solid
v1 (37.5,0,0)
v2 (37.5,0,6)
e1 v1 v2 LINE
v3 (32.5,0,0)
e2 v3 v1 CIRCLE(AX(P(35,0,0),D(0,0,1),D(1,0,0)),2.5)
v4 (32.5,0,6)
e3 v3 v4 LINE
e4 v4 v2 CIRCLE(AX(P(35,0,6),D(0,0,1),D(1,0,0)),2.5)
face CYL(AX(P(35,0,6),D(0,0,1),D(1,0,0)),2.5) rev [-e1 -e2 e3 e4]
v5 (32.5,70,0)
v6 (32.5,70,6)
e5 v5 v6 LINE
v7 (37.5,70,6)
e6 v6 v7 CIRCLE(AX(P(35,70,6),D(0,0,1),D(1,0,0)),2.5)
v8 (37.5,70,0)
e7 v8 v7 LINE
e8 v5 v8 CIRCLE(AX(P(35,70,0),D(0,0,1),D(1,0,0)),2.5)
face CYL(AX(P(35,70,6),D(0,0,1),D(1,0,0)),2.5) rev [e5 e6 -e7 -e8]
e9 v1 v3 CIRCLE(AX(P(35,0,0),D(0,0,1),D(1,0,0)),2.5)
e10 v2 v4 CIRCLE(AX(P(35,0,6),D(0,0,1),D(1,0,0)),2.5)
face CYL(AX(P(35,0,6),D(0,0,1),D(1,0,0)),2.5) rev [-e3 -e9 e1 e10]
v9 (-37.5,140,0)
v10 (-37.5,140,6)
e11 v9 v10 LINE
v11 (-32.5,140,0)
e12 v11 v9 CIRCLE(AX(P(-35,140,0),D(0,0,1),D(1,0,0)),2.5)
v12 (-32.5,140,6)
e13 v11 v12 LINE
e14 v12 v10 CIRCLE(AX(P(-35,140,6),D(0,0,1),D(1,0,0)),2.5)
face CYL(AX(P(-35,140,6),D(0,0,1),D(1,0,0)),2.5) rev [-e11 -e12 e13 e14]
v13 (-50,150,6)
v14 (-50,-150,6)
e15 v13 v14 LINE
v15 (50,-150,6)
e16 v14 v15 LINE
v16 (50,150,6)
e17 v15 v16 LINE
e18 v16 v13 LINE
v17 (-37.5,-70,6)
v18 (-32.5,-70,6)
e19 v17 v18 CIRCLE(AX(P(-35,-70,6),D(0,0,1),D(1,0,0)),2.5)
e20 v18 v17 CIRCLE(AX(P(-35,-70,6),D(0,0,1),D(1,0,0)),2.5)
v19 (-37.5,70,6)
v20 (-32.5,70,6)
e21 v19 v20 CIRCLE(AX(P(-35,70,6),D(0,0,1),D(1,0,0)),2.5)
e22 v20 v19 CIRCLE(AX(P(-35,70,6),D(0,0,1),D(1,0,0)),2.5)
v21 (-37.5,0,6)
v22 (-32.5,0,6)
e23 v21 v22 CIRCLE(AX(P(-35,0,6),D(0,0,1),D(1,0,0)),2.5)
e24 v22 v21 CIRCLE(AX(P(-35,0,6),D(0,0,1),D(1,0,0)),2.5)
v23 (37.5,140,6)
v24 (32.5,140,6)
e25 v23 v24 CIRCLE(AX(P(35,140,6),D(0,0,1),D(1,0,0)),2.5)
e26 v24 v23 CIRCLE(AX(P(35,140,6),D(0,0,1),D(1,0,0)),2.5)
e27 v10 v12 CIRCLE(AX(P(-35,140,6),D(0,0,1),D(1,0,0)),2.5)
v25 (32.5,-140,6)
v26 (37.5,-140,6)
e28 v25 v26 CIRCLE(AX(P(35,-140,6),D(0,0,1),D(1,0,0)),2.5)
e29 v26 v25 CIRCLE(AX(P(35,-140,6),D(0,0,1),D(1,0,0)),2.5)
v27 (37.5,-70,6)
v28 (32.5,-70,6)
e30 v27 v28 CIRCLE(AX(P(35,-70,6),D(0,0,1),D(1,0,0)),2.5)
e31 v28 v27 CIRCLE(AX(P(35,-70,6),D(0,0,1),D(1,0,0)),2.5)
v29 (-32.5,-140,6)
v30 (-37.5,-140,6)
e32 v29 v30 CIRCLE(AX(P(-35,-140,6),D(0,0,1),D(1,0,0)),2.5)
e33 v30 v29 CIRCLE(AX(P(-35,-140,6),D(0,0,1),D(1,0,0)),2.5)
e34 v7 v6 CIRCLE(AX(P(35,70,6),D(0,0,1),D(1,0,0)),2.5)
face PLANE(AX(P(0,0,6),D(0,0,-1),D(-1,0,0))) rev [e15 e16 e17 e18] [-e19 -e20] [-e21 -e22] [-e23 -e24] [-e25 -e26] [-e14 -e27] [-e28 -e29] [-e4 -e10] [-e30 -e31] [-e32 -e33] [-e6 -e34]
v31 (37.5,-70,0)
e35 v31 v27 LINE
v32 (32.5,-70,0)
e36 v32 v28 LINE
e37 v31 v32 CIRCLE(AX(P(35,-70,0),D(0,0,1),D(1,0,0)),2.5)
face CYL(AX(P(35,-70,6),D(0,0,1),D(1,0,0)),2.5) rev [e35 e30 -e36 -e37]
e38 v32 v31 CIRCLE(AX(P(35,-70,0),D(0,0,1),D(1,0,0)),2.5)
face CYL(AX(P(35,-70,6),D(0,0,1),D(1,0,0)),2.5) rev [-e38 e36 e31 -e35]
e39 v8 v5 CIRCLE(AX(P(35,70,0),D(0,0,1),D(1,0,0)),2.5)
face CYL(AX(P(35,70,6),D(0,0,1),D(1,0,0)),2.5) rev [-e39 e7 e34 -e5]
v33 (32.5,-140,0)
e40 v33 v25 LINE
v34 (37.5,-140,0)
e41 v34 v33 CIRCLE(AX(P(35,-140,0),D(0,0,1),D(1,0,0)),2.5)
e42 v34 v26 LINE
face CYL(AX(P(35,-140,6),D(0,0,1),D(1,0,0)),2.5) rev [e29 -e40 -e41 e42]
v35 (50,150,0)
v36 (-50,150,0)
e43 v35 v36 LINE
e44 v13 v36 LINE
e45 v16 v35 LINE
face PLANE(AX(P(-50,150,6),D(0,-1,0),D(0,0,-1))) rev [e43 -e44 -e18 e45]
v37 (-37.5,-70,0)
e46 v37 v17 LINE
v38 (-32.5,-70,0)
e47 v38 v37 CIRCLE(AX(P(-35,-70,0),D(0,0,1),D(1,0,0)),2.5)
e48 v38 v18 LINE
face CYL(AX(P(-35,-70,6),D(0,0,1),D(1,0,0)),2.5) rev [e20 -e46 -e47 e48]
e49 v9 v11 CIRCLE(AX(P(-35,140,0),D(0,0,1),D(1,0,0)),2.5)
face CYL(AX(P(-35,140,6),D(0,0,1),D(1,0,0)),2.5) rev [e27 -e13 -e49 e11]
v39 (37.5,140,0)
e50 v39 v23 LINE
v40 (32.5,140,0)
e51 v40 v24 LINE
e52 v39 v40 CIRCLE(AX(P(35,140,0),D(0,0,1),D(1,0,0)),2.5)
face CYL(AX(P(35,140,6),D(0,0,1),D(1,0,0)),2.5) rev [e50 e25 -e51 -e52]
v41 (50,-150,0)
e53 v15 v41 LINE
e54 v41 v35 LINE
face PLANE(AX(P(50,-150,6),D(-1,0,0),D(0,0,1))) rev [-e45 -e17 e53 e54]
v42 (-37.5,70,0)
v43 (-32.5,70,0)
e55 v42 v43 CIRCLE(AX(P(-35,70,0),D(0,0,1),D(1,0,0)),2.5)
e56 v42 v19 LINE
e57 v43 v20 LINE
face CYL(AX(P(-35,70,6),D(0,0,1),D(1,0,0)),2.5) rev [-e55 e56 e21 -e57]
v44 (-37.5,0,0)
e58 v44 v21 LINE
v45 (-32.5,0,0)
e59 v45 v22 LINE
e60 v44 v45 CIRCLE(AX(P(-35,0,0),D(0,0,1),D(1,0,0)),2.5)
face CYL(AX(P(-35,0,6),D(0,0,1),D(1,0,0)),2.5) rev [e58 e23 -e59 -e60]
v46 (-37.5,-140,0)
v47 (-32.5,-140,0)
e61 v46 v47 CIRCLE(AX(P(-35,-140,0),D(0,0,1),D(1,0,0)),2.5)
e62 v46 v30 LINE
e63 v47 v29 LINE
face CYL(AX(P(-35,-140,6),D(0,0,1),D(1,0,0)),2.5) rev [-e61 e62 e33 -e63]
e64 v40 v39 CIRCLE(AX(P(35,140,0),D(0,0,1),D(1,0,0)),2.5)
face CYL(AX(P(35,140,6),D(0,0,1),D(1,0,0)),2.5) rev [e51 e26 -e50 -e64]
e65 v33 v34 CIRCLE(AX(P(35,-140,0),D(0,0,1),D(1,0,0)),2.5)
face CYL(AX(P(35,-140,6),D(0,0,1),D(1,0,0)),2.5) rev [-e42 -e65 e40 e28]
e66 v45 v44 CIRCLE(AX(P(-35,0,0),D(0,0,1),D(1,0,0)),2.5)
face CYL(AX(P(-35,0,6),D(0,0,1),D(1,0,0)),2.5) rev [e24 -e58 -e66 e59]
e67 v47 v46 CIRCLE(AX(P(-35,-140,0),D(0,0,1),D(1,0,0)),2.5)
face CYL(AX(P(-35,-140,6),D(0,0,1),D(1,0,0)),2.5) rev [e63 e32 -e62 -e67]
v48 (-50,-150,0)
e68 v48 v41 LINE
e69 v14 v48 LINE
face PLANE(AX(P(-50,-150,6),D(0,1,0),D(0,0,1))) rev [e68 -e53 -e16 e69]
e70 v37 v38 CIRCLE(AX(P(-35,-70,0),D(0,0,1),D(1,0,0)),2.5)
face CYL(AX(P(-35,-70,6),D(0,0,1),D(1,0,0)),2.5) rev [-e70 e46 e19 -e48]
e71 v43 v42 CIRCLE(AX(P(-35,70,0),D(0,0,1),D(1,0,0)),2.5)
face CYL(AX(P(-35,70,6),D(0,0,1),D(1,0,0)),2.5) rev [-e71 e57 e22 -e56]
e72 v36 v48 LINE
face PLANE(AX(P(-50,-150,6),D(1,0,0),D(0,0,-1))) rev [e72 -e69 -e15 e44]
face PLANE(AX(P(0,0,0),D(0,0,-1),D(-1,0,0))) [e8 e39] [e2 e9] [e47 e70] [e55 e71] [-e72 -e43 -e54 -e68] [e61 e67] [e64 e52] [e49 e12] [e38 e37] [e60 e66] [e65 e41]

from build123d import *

# Parameters (mm, degrees)
SKETCH1_W            = 100
SKETCH1_H            = 300
BOSS_EXTRUDE1_DEPTH  = 6
M6_TAPPED_HOLE1_D    = 5
LPATTERN1_COUNT      = 3
LPATTERN1_PITCH      = 70
LPATTERN1_COUNT_DIR2 = 2
LPATTERN1_PITCH_DIR2 = 70
LPATTERN2_COUNT      = 3
LPATTERN2_PITCH      = 70
LPATTERN2_COPY_1_D   = 5
LPATTERN2_COPY_2_D   = 5
LPATTERN2_COPY_3_D   = 5
LPATTERN2_COPY_4_D   = 5
LPATTERN2_COPY_5_D   = 5
LPATTERN2_COPY_6_D   = 5
LPATTERN2_COPY_7_D   = 5
LPATTERN2_COPY_8_D   = 5
LPATTERN2_COPY_9_D   = 5
LPATTERN2_COPY_10_D  = 5


with BuildPart() as part:
    # Sketch1 → Boss-Extrude1 (new body)
    with BuildSketch(Plane.XY):
        Rectangle(SKETCH1_W, SKETCH1_H)
    extrude(amount=BOSS_EXTRUDE1_DEPTH)

    # M6 Tapped Hole1 (through all)
    with Locations(Plane.XY.offset(6)):
        with Locations((-35, 0)):
            m6_tapped_hole1 = Hole(M6_TAPPED_HOLE1_D / 2)

    # LPattern1: M6 Tapped Hole1 3 × 2
    with Locations(*[(j * LPATTERN1_PITCH_DIR2, -i * LPATTERN1_PITCH, 0) for i in range(LPATTERN1_COUNT) for j in range(LPATTERN1_COUNT_DIR2) if (i, j) != (0, 0)]):
        add(m6_tapped_hole1, mode=Mode.SUBTRACT)

    # LPattern2: M6 Tapped Hole1 ×3
    with Locations(*[(0, i * LPATTERN2_PITCH, 0) for i in range(1, LPATTERN2_COUNT)]):
        add(m6_tapped_hole1, mode=Mode.SUBTRACT)

    # LPattern2 copy 1 (through all)
    with Locations(Plane(origin=(70, 70, 6), x_dir=(1, 0, 0), z_dir=(0, 0, 1))):
        with Locations((-35, 0)):
            Hole(LPATTERN2_COPY_1_D / 2)

    # LPattern2 copy 2 (through all)
    with Locations(Plane(origin=(70, 140, 6), x_dir=(1, 0, 0), z_dir=(0, 0, 1))):
        with Locations((-35, 0)):
            Hole(LPATTERN2_COPY_2_D / 2)

    # LPattern2 copy 3 (through all)
    with Locations(Plane.XY.offset(6)):
        with Locations((-35, 0)):
            Hole(LPATTERN2_COPY_3_D / 2)

    # LPattern2 copy 4 (through all)
    with Locations(Plane(origin=(0, 70, 6), x_dir=(1, 0, 0), z_dir=(0, 0, 1))):
        with Locations((-35, 0)):
            Hole(LPATTERN2_COPY_4_D / 2)

    # LPattern2 copy 5 (through all)
    with Locations(Plane(origin=(70, 0, 6), x_dir=(1, 0, 0), z_dir=(0, 0, 1))):
        with Locations((-35, 0)):
            Hole(LPATTERN2_COPY_5_D / 2)

    # LPattern2 copy 6 (through all)
    with Locations(Plane(origin=(70, 70, 6), x_dir=(1, 0, 0), z_dir=(0, 0, 1))):
        with Locations((-35, 0)):
            Hole(LPATTERN2_COPY_6_D / 2)

    # LPattern2 copy 7 (through all)
    with Locations(Plane(origin=(0, -70, 6), x_dir=(1, 0, 0), z_dir=(0, 0, 1))):
        with Locations((-35, 0)):
            Hole(LPATTERN2_COPY_7_D / 2)

    # LPattern2 copy 8 (through all)
    with Locations(Plane.XY.offset(6)):
        with Locations((-35, 0)):
            Hole(LPATTERN2_COPY_8_D / 2)

    # LPattern2 copy 9 (through all)
    with Locations(Plane(origin=(70, -70, 6), x_dir=(1, 0, 0), z_dir=(0, 0, 1))):
        with Locations((-35, 0)):
            Hole(LPATTERN2_COPY_9_D / 2)

    # LPattern2 copy 10 (through all)
    with Locations(Plane(origin=(70, 0, 6), x_dir=(1, 0, 0), z_dir=(0, 0, 1))):
        with Locations((-35, 0)):
            Hole(LPATTERN2_COPY_10_D / 2)


solid = part.part
